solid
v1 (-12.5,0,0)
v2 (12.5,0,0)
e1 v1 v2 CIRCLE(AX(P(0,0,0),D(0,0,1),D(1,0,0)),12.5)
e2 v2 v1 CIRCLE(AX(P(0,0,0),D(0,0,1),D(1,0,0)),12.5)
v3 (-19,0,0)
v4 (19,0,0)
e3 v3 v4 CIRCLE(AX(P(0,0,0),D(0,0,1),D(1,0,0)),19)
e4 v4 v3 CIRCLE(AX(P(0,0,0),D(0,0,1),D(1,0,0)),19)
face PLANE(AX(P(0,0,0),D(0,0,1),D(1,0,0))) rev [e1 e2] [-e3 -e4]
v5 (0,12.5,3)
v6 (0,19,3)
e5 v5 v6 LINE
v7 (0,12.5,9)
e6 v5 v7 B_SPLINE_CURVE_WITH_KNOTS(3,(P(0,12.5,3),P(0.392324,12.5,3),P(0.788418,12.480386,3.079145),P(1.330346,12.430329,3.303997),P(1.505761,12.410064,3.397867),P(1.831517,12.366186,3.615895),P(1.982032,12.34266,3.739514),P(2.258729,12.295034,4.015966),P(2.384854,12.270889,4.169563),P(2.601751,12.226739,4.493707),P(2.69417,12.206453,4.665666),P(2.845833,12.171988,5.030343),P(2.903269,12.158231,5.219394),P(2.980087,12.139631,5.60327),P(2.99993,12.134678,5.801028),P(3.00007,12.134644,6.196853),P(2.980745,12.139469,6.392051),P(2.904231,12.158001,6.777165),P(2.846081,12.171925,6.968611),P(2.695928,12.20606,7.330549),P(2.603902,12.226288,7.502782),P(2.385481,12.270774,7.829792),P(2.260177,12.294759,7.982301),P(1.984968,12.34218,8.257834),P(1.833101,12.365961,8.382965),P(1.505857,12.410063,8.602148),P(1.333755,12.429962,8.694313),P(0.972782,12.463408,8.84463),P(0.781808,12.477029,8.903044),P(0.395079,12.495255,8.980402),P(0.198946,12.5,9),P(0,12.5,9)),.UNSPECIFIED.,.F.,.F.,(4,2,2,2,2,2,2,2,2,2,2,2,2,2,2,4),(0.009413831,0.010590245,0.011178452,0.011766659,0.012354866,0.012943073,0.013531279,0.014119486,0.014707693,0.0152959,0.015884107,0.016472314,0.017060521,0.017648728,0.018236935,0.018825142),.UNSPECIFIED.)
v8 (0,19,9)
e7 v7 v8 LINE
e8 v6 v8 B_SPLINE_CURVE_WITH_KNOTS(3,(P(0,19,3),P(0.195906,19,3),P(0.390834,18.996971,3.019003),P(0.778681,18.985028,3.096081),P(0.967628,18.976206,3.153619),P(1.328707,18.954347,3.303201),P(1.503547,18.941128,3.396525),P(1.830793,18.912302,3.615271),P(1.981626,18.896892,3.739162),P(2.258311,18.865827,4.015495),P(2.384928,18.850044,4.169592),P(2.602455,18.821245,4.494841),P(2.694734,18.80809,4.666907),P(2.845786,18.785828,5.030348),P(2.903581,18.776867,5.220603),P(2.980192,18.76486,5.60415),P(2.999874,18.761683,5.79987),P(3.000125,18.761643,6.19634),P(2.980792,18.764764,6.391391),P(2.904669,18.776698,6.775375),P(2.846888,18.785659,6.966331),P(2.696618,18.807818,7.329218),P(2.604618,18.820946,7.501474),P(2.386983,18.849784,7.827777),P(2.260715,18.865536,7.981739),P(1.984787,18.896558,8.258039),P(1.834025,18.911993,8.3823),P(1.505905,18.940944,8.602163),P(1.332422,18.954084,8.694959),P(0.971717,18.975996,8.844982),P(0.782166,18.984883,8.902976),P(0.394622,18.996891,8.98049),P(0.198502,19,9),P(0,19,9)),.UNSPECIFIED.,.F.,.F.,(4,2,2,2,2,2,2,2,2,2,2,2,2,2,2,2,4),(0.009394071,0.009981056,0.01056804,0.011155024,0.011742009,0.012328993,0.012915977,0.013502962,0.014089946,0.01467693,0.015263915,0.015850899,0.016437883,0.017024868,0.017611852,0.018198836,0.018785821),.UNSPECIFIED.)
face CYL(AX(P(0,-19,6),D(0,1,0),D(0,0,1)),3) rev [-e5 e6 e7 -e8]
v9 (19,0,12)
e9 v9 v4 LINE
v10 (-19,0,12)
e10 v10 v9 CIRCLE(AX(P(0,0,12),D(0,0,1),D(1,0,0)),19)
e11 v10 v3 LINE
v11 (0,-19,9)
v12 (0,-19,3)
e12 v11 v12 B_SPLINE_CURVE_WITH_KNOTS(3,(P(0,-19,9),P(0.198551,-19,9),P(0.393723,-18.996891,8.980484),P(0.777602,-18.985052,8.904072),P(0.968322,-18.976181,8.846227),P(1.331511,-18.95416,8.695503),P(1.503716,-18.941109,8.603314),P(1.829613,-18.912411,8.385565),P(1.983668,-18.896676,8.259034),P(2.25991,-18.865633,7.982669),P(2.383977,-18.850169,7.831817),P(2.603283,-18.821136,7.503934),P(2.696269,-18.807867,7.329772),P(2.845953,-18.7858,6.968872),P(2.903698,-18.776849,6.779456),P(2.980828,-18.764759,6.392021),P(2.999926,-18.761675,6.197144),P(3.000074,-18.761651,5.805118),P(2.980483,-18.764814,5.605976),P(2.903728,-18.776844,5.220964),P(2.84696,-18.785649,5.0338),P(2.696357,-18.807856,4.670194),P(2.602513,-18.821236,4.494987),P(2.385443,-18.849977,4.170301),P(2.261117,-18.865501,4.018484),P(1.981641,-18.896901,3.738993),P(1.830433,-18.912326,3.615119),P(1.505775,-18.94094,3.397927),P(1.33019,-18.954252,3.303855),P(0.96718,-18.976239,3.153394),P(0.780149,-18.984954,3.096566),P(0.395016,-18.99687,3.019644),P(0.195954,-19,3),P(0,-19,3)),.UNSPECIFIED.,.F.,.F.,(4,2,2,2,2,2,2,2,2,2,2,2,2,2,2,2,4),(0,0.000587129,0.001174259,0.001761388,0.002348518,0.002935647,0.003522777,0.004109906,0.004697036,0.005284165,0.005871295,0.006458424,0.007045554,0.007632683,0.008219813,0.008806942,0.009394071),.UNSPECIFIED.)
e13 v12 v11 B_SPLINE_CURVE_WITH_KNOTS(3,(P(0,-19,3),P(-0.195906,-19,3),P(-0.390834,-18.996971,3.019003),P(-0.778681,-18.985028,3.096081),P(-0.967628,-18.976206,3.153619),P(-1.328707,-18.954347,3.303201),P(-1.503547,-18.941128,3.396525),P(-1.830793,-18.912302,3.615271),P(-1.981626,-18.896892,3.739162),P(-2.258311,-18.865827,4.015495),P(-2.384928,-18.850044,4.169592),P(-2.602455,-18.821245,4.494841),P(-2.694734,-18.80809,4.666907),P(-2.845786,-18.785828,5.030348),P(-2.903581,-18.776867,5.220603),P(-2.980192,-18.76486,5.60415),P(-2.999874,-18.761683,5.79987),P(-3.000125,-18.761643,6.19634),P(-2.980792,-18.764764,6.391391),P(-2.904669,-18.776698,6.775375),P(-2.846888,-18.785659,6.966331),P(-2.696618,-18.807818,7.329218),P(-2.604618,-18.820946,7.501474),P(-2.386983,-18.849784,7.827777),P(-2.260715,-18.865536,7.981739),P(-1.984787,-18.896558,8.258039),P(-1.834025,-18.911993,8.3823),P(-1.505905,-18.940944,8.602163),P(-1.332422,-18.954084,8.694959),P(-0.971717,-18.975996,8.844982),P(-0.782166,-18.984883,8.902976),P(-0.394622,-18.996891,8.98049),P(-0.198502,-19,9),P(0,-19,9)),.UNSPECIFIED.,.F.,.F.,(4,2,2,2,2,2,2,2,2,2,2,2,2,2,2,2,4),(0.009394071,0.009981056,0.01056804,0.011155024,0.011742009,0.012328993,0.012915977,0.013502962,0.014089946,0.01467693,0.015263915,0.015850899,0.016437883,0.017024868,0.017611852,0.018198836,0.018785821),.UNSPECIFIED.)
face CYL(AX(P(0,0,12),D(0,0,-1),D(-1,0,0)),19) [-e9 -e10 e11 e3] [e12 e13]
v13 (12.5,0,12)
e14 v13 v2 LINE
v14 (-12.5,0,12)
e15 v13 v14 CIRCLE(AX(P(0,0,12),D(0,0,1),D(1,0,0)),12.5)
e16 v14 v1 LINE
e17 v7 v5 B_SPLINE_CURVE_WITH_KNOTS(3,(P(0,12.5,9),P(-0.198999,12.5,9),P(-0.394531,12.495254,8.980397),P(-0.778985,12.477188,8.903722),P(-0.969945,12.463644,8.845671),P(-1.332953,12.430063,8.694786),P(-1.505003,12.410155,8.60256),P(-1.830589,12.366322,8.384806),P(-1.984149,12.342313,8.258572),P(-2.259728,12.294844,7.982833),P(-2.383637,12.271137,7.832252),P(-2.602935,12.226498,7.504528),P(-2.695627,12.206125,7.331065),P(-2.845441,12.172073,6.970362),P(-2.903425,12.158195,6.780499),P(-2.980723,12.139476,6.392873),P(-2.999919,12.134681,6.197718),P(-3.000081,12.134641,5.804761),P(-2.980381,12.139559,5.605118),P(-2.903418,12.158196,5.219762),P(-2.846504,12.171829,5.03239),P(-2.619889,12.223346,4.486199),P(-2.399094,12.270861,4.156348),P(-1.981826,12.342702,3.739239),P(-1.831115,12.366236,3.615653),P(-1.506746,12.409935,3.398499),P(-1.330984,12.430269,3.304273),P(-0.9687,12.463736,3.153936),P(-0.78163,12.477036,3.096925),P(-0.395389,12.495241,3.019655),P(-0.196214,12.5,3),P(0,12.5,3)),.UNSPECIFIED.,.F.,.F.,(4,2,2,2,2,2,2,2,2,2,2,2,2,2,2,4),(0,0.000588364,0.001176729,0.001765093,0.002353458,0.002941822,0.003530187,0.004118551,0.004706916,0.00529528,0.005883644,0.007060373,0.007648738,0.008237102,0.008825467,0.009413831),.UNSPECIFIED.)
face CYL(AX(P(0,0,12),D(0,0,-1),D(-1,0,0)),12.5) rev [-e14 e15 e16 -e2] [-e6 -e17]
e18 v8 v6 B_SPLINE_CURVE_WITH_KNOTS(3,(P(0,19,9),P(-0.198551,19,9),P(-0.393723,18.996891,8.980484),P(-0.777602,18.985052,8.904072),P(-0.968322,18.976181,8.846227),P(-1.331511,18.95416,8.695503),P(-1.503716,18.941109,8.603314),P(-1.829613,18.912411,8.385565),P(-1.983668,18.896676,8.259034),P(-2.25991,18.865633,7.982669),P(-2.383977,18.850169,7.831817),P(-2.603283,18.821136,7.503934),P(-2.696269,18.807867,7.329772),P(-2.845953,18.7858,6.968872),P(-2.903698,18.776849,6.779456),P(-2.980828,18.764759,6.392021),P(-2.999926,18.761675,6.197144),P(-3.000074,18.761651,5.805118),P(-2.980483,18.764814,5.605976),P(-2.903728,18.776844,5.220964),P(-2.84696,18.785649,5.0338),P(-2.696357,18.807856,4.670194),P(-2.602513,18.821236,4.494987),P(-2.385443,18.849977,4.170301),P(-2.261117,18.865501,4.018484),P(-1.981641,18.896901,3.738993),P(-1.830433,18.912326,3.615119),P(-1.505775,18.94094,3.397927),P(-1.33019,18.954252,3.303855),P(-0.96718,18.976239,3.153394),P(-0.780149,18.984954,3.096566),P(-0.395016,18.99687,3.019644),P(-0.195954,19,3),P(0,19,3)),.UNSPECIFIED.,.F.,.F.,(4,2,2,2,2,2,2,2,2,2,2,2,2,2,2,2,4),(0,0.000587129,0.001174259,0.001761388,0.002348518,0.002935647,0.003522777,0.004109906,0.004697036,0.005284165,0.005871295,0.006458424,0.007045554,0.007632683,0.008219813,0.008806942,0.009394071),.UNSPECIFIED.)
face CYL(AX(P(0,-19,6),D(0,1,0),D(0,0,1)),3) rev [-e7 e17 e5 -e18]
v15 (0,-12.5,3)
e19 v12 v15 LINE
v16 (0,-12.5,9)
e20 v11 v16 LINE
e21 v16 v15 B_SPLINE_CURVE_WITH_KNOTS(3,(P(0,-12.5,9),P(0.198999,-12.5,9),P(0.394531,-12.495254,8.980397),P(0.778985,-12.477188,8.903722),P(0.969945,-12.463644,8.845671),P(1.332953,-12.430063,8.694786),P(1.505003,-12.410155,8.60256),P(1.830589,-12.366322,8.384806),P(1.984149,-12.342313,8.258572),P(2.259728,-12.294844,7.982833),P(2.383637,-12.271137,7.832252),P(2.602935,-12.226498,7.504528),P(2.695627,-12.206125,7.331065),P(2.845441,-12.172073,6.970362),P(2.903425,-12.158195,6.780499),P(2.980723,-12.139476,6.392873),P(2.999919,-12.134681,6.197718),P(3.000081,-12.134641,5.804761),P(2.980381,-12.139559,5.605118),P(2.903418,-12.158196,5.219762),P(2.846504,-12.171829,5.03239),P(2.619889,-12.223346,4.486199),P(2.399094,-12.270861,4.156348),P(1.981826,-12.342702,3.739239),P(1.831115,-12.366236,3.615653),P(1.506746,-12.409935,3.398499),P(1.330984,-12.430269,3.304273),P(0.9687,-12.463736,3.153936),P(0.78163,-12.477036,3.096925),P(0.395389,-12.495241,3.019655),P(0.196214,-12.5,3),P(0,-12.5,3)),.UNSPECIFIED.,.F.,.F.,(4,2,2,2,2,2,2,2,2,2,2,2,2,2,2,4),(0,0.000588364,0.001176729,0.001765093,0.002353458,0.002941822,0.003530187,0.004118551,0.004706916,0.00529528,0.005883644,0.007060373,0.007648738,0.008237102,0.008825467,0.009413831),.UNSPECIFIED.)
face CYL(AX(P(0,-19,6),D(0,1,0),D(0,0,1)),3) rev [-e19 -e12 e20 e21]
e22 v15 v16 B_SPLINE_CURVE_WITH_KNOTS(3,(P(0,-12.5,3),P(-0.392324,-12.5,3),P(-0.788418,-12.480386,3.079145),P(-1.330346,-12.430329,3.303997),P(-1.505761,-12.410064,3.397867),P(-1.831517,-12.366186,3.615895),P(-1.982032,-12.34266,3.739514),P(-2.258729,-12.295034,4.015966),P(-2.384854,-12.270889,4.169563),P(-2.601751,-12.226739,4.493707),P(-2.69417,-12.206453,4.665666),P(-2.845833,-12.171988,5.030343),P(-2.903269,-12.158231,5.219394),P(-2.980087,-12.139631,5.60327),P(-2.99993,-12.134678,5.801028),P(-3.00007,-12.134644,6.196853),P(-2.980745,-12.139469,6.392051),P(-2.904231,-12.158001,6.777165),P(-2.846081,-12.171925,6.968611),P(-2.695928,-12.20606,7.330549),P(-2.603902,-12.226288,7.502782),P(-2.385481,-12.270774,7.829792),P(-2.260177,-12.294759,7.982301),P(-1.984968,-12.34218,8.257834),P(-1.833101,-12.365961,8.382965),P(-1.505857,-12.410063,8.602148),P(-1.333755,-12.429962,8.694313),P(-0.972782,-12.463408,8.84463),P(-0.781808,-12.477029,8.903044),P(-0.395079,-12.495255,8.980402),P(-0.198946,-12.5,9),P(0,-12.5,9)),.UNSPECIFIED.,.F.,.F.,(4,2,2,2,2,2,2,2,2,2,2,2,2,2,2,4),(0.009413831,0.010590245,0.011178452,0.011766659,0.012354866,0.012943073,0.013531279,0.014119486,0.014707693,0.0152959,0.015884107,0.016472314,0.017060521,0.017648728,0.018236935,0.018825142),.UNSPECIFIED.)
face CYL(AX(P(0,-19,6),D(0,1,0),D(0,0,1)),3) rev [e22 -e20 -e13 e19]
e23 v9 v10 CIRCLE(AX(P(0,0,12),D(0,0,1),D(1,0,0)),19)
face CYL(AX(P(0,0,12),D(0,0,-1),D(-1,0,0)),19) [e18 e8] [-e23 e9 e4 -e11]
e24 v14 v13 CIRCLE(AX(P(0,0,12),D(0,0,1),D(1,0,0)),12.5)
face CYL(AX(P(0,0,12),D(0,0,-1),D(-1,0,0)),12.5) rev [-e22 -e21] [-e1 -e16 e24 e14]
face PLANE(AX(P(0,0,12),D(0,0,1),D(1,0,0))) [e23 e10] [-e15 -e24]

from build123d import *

# Parameters (mm, degrees)
COLLAR_RING_SKETCH_R     = 19
COLLAR_RING_SKETCH_R_2   = 12.5
COLLAR_RING_38X_25_DEPTH = 12
CROSS_HOLE_6_DEPTH       = 30.427877939
CROSS_HOLE_6_DEPTH_BACK  = 30.427877939
CROSS_HOLE_SKETCH_R      = 3


with BuildPart() as part:
    # Collar Ring Sketch → Collar Ring Ø38xØ25 (new body)
    with BuildSketch(Plane.XY):
        Circle(COLLAR_RING_SKETCH_R)
        Circle(COLLAR_RING_SKETCH_R_2, mode=Mode.SUBTRACT)
    extrude(amount=COLLAR_RING_38X_25_DEPTH)

    # Cross Hole Sketch → Cross Hole Ø6 (cut, two sides: drawn at the far end of the back side and taken through both)
    with BuildSketch(Plane(origin=(0, 0, 0), x_dir=(1, 0, 0), z_dir=(0, 1, 0)).offset(-CROSS_HOLE_6_DEPTH_BACK)):
        with Locations(Location((0, -6, 0), (0, 0, 270))):
            Circle(CROSS_HOLE_SKETCH_R)
    extrude(amount=CROSS_HOLE_6_DEPTH + CROSS_HOLE_6_DEPTH_BACK, mode=Mode.SUBTRACT)


solid = part.part
